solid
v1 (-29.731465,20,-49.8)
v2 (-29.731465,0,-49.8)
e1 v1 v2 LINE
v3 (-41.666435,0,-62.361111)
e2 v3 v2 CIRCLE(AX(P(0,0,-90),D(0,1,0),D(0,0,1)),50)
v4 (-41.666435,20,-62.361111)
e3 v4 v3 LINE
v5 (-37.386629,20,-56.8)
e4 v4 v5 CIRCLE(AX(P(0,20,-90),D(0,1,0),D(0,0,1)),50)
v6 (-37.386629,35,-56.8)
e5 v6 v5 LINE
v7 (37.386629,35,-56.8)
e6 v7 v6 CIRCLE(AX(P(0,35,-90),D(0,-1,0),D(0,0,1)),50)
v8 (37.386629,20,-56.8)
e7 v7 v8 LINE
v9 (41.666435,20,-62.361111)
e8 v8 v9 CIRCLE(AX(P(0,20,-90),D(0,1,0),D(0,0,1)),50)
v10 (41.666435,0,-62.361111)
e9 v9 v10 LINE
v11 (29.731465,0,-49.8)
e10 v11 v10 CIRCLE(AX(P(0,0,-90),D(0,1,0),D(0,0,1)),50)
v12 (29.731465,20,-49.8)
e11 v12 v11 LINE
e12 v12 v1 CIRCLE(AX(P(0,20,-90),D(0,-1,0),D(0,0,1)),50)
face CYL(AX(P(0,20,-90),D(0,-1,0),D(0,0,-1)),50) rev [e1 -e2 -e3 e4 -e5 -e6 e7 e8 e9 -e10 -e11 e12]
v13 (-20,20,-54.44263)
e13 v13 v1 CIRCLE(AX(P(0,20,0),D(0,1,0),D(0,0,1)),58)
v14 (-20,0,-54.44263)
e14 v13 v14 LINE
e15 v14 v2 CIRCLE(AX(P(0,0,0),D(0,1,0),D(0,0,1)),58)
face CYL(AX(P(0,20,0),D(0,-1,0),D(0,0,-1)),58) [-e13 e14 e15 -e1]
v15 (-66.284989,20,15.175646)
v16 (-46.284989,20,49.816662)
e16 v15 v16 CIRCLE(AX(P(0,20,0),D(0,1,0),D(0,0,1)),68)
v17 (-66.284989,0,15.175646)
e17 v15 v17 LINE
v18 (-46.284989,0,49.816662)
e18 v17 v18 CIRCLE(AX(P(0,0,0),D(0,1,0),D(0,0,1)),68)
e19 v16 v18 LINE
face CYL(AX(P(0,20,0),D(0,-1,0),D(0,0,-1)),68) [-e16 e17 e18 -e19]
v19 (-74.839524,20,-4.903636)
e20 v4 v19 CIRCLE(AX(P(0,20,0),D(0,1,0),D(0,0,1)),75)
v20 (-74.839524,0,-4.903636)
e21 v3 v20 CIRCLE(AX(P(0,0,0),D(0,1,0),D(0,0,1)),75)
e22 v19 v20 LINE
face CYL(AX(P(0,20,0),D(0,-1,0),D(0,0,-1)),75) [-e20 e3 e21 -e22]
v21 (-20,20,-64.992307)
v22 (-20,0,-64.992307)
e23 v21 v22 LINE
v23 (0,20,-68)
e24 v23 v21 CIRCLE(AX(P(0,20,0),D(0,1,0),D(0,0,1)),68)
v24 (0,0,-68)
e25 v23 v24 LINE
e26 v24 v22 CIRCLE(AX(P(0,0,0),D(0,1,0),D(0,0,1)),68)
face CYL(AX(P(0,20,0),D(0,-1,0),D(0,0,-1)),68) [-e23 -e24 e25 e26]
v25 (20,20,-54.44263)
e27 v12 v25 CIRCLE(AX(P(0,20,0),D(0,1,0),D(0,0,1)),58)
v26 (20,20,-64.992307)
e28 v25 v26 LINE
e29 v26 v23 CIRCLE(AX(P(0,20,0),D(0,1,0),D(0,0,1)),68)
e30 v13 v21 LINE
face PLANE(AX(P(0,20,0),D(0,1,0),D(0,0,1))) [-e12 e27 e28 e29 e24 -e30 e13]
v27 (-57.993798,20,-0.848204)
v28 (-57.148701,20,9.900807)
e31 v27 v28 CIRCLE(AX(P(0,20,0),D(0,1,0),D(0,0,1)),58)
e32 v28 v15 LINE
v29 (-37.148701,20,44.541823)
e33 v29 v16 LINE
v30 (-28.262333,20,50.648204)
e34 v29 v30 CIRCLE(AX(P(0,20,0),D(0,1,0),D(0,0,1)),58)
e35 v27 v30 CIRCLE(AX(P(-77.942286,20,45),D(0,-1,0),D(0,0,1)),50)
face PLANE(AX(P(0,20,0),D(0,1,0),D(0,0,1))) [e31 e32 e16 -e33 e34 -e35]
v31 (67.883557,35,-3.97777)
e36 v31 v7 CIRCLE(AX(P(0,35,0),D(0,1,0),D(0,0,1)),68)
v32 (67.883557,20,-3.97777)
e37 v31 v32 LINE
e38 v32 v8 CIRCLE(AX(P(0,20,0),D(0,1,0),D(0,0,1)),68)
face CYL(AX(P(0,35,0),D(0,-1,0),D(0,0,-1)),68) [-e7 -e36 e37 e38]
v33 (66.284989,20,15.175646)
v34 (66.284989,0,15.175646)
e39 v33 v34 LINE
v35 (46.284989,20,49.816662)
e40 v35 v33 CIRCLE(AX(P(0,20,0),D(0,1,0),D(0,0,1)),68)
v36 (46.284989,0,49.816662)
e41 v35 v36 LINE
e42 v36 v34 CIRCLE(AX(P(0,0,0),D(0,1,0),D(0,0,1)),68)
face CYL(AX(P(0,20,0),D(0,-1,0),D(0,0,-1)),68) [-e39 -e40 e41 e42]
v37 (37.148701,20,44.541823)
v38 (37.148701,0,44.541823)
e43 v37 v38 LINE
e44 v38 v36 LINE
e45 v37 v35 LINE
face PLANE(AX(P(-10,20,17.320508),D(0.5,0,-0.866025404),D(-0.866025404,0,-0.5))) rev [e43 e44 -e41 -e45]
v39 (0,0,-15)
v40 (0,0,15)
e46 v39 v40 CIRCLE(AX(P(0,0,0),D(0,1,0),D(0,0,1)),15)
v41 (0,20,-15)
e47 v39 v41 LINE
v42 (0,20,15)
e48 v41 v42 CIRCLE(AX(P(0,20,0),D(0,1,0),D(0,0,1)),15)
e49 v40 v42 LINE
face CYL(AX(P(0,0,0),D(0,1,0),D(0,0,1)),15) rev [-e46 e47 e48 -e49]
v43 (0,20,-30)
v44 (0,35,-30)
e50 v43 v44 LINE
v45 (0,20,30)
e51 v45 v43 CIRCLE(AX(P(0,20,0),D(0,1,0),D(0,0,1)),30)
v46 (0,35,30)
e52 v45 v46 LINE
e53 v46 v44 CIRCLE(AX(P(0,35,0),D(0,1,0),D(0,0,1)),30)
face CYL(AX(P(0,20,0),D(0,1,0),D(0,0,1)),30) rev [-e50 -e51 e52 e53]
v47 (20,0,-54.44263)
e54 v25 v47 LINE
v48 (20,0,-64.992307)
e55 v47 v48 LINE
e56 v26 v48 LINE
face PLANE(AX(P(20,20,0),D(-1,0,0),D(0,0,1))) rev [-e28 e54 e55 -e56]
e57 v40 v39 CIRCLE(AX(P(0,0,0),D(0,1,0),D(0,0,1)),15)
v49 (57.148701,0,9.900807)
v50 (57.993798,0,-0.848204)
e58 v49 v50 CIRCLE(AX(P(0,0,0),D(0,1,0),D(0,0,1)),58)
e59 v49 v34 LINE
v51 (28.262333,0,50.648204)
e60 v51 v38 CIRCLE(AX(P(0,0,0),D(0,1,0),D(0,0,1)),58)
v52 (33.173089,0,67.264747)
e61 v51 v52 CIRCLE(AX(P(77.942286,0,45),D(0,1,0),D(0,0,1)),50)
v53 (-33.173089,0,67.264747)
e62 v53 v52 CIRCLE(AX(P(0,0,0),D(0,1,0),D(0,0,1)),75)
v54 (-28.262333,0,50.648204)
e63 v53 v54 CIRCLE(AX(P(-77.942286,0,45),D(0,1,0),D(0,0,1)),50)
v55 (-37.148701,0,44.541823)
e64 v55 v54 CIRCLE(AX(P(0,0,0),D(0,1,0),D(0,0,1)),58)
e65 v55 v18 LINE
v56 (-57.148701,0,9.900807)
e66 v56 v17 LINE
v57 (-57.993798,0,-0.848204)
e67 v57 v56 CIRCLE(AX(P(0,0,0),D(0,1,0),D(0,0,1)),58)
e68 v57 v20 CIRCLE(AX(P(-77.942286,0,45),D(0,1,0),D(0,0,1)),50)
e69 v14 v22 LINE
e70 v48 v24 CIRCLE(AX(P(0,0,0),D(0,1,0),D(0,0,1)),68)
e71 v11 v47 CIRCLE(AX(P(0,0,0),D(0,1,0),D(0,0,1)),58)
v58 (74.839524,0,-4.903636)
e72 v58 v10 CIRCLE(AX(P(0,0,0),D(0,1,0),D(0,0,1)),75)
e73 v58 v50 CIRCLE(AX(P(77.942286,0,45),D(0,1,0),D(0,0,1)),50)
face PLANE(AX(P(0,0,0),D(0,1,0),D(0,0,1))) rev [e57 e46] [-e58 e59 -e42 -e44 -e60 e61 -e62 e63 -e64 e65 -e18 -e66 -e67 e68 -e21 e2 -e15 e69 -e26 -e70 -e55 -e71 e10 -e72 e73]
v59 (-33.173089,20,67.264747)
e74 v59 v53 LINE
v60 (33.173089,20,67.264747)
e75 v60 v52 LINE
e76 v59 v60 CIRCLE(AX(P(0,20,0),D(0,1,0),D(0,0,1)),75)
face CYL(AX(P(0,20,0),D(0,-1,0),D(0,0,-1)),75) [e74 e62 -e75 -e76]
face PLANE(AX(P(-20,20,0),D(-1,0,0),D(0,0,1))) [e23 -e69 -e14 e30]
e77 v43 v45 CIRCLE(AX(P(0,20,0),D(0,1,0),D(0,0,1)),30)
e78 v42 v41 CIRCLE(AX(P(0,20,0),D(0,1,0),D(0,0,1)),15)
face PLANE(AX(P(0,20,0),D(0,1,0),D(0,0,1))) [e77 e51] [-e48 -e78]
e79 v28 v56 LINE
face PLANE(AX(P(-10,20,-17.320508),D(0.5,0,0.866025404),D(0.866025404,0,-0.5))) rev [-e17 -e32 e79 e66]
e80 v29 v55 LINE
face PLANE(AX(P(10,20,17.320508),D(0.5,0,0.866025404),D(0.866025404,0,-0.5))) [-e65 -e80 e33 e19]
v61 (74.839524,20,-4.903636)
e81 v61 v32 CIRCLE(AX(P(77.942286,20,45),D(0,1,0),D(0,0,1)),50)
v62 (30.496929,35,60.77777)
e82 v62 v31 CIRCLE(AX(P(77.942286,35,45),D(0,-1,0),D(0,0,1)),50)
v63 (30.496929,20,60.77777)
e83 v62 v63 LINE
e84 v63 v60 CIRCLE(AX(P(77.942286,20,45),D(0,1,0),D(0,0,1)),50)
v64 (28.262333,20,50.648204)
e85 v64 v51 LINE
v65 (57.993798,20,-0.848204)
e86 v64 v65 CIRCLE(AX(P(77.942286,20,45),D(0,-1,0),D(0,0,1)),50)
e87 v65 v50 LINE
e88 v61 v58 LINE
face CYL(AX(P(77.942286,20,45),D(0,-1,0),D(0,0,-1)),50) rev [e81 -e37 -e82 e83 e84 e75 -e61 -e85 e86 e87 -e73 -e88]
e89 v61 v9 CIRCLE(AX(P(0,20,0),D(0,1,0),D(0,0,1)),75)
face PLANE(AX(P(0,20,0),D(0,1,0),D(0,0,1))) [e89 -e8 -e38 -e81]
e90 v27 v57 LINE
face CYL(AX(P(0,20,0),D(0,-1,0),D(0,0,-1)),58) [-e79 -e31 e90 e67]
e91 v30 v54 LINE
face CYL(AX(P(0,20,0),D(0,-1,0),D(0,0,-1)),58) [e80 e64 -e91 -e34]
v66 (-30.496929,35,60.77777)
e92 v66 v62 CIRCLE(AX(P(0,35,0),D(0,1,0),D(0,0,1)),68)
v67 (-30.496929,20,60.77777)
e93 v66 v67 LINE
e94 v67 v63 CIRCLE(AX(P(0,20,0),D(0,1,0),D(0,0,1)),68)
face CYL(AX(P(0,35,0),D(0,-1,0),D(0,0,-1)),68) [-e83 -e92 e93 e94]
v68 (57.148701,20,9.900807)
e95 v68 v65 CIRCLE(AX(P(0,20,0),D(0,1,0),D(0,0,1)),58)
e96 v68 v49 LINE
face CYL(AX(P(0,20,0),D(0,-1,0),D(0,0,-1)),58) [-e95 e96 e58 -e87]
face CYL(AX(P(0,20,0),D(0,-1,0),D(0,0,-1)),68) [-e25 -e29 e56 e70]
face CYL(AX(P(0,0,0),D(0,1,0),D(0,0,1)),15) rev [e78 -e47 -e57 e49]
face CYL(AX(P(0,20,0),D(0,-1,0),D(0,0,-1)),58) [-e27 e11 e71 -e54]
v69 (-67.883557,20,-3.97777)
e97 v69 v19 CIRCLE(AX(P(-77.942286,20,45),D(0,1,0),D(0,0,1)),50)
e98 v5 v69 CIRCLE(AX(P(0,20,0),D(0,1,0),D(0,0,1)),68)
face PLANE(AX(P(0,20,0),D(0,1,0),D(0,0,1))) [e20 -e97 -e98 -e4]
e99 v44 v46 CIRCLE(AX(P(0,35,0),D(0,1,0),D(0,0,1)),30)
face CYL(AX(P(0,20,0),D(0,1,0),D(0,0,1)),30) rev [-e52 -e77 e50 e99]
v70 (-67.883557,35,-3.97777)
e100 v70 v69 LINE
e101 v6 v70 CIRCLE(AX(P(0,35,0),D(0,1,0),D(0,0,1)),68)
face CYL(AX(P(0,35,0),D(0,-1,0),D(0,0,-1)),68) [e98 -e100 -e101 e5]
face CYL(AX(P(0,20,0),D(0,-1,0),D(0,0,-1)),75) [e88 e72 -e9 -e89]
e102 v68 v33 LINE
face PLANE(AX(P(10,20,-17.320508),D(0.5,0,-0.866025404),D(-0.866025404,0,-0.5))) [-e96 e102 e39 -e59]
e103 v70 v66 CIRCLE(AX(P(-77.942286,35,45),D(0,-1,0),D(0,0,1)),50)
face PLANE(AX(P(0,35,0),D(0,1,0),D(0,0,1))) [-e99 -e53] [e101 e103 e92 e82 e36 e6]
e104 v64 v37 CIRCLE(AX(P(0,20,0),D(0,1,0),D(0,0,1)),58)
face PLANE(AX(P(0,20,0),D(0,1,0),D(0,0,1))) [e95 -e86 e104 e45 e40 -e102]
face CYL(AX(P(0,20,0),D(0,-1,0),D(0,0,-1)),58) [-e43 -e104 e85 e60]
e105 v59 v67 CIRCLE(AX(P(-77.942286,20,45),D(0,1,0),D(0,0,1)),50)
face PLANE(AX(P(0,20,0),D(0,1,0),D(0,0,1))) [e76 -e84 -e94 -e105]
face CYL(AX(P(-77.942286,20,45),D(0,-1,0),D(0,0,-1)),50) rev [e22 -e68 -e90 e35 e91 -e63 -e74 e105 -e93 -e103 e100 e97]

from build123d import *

# Parameters (mm, degrees)
BASE_LOBE_PLATE_20MM_DEPTH = 20
UPPER_LOBE_BOSS_15MM_DEPTH = 15
COUNTERBORE_SKETCH_60_R    = 30
COUNTERBORE_60X15_DEPTH    = 15
THROUGH_HOLE_SKETCH_30_R   = 15
THROUGH_HOLE_30_DEPTH      = 108.823718893


with BuildPart() as part:
    # Base Lobe Profile Sketch → Base Lobe Plate 20mm (new body)
    with BuildSketch(Plane(origin=(0, 0, 0), x_dir=(1, 0, 0), z_dir=(0, 1, 0))):
        with BuildLine():
            ThreePointArc((74.839524023, 4.903635799), (34.641016151, -20), (33.173088838, -67.264746911))
            ThreePointArc((33.173088838, -67.264746911), (0, -75), (-33.173088838, -67.264746911))
            ThreePointArc((-33.173088838, -67.264746911), (-34.641016151, -20), (-74.839524023, 4.903635799))
            ThreePointArc((-74.839524023, 4.903635799), (-64.951905284, 37.5), (-41.666435185, 62.361111111))
            ThreePointArc((-41.666435185, 62.361111111), (0, 40), (41.666435185, 62.361111111))
            ThreePointArc((41.666435185, 62.361111111), (64.951905284, 37.5), (74.839524023, 4.903635799))
        make_face()
        with BuildLine():
            ThreePointArc((-28.262332701, -50.648203821), (-34.641016151, -20), (-57.993797516, 0.848203821))
            ThreePointArc((-57.993797516, 0.848203821), (-57.821570771, -4.545982138), (-57.148700937, -9.900807102))
            Line((-57.148700937, -9.900807102), (-66.284989118, -15.175645543))
            ThreePointArc((-66.284989118, -15.175645543), (-58.889727457, -34), (-46.284989118, -49.816661694))
            Line((-46.284989118, -49.816661694), (-37.148700937, -44.541823253))
            ThreePointArc((-37.148700937, -44.541823253), (-32.847721402, -47.801958105), (-28.262332701, -50.648203821))
        make_face()
        with BuildLine():
            ThreePointArc((57.148700937, -9.900807102), (57.821570771, -4.545982138), (57.993797516, 0.848203821))
            ThreePointArc((57.993797516, 0.848203821), (34.641016151, -20), (28.262332701, -50.648203821))
            ThreePointArc((28.262332701, -50.648203821), (32.847721402, -47.801958105), (37.148700937, -44.541823253))
            Line((37.148700937, -44.541823253), (46.284989118, -49.816661694))
            ThreePointArc((46.284989118, -49.816661694), (58.889727457, -34), (66.284989118, -15.175645543))
            Line((66.284989118, -15.175645543), (57.148700937, -9.900807102))
        make_face()
        with BuildLine():
            ThreePointArc((29.731464814, 49.8), (24.973849369, 52.347940243), (20, 54.442630355))
            Line((20, 54.442630355), (20, 64.992307237))
            ThreePointArc((20, 64.992307237), (0, 68), (-20, 64.992307237))
            Line((-20, 64.992307237), (-20, 54.442630355))
            ThreePointArc((-20, 54.442630355), (-24.973849369, 52.347940243), (-29.731464814, 49.8))
            ThreePointArc((-29.731464814, 49.8), (0, 40), (29.731464814, 49.8))
        make_face()
    extrude(amount=BASE_LOBE_PLATE_20MM_DEPTH)

    # Upper Lobe Profile Sketch → Upper Lobe Boss 15mm (add)
    with BuildSketch(Plane(origin=(0, 20, 0), x_dir=(1, 0, 0), z_dir=(0, 1, 0))):
        with BuildLine():
            ThreePointArc((57.993797516, 0.848203821), (62.857299495, 2.670149694), (67.883557248, 3.977770152))
            ThreePointArc((67.883557248, 3.977770152), (58.889727457, 34), (37.386628626, 56.8))
            ThreePointArc((37.386628626, 56.8), (33.741067214, 53.100943329), (29.731464814, 49.8))
            ThreePointArc((29.731464814, 49.8), (0, 40), (-29.731464814, 49.8))
            ThreePointArc((-29.731464814, 49.8), (-33.741067214, 53.100943329), (-37.386628626, 56.8))
            ThreePointArc((-37.386628626, 56.8), (-58.889727457, 34), (-67.883557248, 3.977770152))
            ThreePointArc((-67.883557248, 3.977770152), (-62.857299495, 2.670149694), (-57.993797516, 0.848203821))
            ThreePointArc((-57.993797516, 0.848203821), (-34.641016151, -20), (-28.262332701, -50.648203821))
            ThreePointArc((-28.262332701, -50.648203821), (-29.11623228, -55.771093023), (-30.496928622, -60.777770152))
            ThreePointArc((-30.496928622, -60.777770152), (0, -68), (30.496928622, -60.777770152))
            ThreePointArc((30.496928622, -60.777770152), (29.11623228, -55.771093023), (28.262332701, -50.648203821))
            ThreePointArc((28.262332701, -50.648203821), (34.641016151, -20), (57.993797516, 0.848203821))
        make_face()
    extrude(amount=UPPER_LOBE_BOSS_15MM_DEPTH)

    # Counterbore Sketch Ø60 → Counterbore Ø60x15 (cut)
    with BuildSketch(Plane(origin=(0, 35, 0), x_dir=(1, 0, 0), z_dir=(0, 1, 0))):
        with Locations(Location((0, 0, 0), (0, 0, 270))):
            Circle(COUNTERBORE_SKETCH_60_R)
    extrude(amount=-COUNTERBORE_60X15_DEPTH, mode=Mode.SUBTRACT)

    # Through Hole Sketch Ø30 → Through Hole Ø30 (cut, through all)
    with BuildSketch(Plane(origin=(0, 20, 0), x_dir=(1, 0, 0), z_dir=(0, 1, 0))):
        with Locations(Location((0, 0, 0), (0, 0, 270))):
            Circle(THROUGH_HOLE_SKETCH_30_R)
    extrude(amount=-THROUGH_HOLE_30_DEPTH, mode=Mode.SUBTRACT)


solid = part.part
